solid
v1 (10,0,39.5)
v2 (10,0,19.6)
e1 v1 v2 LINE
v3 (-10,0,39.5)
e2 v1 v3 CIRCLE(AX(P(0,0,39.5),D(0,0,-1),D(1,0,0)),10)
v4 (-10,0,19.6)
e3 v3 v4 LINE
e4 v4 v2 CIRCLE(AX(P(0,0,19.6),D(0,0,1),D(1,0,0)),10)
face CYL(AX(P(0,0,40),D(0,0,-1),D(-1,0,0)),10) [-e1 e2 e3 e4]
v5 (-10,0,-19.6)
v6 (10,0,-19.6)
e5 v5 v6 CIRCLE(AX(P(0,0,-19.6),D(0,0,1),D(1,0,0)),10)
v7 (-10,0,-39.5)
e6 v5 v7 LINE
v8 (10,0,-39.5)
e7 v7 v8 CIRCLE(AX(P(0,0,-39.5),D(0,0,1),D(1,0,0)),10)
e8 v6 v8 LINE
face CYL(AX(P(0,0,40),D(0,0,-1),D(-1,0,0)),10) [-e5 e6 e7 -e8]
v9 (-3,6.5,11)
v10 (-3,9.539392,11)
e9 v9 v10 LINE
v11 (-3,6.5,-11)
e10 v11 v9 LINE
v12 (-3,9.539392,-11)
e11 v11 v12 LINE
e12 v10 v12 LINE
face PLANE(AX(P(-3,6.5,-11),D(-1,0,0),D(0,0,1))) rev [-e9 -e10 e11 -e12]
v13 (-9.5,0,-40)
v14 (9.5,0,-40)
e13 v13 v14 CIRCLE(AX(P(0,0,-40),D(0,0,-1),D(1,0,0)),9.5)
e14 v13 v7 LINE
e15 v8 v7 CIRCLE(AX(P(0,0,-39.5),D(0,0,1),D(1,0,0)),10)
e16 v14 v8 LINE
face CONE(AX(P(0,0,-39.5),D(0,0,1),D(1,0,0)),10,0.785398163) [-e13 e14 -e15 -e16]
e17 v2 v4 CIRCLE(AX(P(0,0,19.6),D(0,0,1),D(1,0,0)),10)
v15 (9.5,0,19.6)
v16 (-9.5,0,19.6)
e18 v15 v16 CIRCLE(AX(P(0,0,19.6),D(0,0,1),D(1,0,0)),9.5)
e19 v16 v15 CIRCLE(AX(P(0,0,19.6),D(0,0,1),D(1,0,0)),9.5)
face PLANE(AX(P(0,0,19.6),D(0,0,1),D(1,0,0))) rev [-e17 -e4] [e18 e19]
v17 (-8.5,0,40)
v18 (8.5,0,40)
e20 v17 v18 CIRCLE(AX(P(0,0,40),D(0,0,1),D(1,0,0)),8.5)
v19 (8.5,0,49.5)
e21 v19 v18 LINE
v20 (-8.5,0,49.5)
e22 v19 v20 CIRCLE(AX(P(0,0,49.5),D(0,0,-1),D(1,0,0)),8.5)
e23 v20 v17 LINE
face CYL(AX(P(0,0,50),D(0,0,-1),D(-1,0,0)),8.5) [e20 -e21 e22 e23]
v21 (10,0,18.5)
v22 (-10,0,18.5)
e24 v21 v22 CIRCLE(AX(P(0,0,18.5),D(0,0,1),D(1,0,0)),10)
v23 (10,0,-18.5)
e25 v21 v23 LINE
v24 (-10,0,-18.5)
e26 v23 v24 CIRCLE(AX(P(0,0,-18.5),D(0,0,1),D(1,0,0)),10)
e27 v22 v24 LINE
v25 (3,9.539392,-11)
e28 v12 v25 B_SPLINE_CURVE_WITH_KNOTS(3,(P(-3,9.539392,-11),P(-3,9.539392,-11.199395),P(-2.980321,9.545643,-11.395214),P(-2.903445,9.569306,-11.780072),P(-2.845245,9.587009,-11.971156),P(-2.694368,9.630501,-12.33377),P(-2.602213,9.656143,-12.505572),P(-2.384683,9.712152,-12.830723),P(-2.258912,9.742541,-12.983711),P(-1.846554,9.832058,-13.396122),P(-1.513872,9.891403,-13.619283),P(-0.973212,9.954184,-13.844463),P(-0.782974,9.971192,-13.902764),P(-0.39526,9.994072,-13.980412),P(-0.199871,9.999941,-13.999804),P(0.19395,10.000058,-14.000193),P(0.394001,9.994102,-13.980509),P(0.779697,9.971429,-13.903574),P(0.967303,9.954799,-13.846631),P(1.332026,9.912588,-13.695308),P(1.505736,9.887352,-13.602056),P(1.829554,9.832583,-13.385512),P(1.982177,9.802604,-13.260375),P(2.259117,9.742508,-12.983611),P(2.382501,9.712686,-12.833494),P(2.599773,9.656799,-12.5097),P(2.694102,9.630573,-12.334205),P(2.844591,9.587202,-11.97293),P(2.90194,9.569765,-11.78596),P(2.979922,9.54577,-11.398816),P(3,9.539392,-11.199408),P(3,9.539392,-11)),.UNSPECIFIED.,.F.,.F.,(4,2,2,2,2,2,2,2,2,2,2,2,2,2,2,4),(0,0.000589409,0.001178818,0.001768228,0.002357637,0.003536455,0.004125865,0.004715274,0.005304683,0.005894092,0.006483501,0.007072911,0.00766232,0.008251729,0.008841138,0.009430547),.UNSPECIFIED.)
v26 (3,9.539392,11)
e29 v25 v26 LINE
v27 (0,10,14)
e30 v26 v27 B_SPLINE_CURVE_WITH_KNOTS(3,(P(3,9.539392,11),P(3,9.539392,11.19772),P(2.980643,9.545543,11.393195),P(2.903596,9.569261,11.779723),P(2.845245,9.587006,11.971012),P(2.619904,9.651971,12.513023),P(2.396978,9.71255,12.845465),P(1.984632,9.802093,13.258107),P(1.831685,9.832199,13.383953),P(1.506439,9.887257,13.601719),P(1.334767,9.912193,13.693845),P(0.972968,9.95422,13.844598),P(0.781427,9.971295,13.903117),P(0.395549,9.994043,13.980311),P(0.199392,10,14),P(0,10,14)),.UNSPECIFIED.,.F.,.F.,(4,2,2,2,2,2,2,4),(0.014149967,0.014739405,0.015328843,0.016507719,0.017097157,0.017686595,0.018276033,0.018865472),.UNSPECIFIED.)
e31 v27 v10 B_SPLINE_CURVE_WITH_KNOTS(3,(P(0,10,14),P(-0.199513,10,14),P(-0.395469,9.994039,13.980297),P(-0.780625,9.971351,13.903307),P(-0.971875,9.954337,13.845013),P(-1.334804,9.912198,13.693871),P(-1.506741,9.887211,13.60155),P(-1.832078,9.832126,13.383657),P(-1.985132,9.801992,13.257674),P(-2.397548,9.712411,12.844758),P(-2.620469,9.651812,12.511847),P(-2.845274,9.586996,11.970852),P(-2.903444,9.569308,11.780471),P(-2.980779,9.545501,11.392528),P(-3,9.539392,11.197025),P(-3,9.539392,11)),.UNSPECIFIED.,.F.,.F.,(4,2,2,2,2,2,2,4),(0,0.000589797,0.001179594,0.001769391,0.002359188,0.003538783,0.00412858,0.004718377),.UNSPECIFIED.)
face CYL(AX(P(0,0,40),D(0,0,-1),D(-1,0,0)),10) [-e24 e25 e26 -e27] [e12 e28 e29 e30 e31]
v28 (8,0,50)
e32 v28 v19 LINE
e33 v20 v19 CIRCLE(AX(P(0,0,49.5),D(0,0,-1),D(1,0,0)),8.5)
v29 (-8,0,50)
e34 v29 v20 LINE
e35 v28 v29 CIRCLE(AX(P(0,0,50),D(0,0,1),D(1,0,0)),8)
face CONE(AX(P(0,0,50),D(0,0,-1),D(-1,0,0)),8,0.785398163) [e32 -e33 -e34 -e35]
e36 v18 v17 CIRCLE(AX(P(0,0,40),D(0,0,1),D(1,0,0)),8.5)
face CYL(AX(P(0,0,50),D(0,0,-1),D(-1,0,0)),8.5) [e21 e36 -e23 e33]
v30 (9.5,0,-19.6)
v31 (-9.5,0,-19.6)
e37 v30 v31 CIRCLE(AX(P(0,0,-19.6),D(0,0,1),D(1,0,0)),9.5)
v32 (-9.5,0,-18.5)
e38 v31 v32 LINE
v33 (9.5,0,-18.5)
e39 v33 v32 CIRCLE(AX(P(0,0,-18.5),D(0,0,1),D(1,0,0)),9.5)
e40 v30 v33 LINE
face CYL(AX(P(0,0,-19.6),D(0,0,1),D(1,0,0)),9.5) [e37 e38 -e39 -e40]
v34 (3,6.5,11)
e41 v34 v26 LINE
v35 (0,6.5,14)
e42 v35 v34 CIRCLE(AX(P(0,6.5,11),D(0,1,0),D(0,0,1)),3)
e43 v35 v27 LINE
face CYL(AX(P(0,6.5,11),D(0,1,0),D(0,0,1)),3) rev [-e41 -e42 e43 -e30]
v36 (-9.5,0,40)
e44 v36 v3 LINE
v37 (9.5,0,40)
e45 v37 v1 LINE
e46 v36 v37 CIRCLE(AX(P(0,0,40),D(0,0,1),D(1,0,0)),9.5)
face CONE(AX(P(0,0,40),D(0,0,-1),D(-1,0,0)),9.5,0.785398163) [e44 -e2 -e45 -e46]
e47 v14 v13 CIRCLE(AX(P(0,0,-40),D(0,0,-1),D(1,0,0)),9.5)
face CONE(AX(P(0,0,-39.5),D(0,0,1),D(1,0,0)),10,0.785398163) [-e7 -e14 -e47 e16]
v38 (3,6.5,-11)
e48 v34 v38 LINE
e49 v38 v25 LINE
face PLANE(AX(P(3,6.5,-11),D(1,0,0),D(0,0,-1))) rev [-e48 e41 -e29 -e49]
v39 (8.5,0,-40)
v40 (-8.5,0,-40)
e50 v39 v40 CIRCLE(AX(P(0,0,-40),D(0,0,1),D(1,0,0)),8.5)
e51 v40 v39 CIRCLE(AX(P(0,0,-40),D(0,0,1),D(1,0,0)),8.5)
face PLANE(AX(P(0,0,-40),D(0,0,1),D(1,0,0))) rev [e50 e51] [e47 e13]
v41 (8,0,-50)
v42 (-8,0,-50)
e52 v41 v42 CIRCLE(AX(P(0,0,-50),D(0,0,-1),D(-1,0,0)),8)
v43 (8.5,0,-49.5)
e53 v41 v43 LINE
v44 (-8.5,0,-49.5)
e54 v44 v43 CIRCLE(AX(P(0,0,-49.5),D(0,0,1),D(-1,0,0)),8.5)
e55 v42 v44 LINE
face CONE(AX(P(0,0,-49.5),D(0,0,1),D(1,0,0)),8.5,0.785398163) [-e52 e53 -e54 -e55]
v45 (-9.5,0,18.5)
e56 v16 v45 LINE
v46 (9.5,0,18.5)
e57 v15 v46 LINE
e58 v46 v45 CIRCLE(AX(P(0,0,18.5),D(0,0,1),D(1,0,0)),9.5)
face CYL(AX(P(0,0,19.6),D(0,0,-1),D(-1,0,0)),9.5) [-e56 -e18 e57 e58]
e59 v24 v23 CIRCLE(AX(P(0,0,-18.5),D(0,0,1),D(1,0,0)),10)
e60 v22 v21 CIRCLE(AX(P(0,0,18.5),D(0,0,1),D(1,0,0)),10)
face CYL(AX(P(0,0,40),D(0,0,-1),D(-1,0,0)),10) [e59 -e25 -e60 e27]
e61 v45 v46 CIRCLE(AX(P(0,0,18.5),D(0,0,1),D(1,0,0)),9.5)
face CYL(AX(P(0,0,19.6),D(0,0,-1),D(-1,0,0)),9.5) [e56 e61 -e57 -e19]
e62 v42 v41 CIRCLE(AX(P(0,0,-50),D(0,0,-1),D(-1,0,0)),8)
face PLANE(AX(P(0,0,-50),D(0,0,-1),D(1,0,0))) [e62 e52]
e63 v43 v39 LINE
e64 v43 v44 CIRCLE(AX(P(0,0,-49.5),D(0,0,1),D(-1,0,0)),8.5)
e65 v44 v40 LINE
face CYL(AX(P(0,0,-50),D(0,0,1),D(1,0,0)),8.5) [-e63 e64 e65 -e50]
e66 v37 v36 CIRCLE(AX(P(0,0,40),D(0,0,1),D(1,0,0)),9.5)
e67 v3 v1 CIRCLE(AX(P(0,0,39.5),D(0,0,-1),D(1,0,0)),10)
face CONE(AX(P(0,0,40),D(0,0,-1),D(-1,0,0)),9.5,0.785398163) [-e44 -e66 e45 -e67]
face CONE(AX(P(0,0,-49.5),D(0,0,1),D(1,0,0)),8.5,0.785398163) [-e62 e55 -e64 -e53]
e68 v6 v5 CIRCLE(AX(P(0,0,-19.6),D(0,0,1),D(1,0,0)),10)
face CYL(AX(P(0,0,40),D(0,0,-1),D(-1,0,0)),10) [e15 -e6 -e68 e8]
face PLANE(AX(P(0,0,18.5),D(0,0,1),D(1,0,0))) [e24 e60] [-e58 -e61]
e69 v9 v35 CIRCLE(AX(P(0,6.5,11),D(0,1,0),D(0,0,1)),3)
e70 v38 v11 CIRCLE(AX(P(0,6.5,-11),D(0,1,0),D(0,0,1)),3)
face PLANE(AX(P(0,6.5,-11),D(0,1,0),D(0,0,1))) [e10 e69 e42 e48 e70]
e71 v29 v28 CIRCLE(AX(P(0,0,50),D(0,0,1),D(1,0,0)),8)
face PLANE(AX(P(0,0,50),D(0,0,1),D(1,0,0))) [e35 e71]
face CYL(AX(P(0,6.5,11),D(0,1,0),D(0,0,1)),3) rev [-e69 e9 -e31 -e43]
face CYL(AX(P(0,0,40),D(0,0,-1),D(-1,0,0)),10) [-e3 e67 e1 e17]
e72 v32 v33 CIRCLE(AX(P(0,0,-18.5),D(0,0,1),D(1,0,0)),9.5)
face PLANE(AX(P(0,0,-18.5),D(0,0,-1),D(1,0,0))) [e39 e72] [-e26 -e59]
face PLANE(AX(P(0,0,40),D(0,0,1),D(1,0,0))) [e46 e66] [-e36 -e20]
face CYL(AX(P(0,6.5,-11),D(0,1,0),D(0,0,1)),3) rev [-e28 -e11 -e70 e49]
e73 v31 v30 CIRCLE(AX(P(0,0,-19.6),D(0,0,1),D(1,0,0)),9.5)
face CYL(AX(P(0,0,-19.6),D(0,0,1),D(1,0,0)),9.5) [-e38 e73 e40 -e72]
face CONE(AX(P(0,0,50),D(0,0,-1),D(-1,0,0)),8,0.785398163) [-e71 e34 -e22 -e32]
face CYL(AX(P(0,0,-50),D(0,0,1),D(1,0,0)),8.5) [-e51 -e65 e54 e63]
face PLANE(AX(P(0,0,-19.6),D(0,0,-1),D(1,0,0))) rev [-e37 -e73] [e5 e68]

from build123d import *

# Parameters (mm, degrees)
SKETCH_1_R          = 10
EXTRUDE_1_DEPTH     = 40
SKETCH_2_R          = 8.5
EXTRUDE_2_DEPTH     = 10
CUT_EXTRUDE_START   = 1.1
SKETCH_4_R          = 10
SKETCH_4_R_2        = 9.5
CUT_EXTRUDE_1_DEPTH = 1.1
CHAMFER_1_SIZE      = 0.5
CUT_EXTRUDE_2_DEPTH = 3.5


with BuildPart() as part:
    # 草图1 → 凸台-拉伸1 (new, symmetric)
    with BuildSketch(Plane.XY):
        Circle(SKETCH_1_R)
    extrude(amount=EXTRUDE_1_DEPTH, both=True)

    # 草图2 → 凸台-拉伸2 (add)
    with BuildSketch(Plane.XY.offset(40)):
        Circle(SKETCH_2_R)
    extrude_2 = extrude(amount=EXTRUDE_2_DEPTH)

    # 草图4 → 切除-拉伸1 (cut)
    with BuildSketch(Plane.XY.offset(18.5).offset(CUT_EXTRUDE_START)):
        Circle(SKETCH_4_R)
        Circle(SKETCH_4_R_2, mode=Mode.SUBTRACT)
    cut_extrude_1 = extrude(amount=-CUT_EXTRUDE_1_DEPTH, mode=Mode.SUBTRACT)

    # 镜向1: 凸台-拉伸2, 切除-拉伸1 across plane
    add(extrude_2.mirror(Plane.XY))
    add(cut_extrude_1.mirror(Plane.XY), mode=Mode.SUBTRACT)

    # 倒角1
    chamfer_1_edges = [part.edges().sort_by_distance(p)[0] for p in [
        (-8.5, 0, -50),
        (-10, 0, -40),
        (-10, 0, 40),
        (-8.5, 0, 50),
    ]]
    chamfer(chamfer_1_edges, length=CHAMFER_1_SIZE)

    # 草图5 → 切除-拉伸2 (cut)
    with BuildSketch(Plane(origin=(0, 10, 0), x_dir=(1, 0, 0), z_dir=(0, 1, 0))):
        with BuildLine():
            Line((3, 11), (3, -11))
            ThreePointArc((3, -11), (0, -14), (-3, -11))
            Line((-3, -11), (-3, 11))
            ThreePointArc((-3, 11), (0, 14), (3, 11))
        make_face()
    extrude(amount=-CUT_EXTRUDE_2_DEPTH, mode=Mode.SUBTRACT)


solid = part.part
